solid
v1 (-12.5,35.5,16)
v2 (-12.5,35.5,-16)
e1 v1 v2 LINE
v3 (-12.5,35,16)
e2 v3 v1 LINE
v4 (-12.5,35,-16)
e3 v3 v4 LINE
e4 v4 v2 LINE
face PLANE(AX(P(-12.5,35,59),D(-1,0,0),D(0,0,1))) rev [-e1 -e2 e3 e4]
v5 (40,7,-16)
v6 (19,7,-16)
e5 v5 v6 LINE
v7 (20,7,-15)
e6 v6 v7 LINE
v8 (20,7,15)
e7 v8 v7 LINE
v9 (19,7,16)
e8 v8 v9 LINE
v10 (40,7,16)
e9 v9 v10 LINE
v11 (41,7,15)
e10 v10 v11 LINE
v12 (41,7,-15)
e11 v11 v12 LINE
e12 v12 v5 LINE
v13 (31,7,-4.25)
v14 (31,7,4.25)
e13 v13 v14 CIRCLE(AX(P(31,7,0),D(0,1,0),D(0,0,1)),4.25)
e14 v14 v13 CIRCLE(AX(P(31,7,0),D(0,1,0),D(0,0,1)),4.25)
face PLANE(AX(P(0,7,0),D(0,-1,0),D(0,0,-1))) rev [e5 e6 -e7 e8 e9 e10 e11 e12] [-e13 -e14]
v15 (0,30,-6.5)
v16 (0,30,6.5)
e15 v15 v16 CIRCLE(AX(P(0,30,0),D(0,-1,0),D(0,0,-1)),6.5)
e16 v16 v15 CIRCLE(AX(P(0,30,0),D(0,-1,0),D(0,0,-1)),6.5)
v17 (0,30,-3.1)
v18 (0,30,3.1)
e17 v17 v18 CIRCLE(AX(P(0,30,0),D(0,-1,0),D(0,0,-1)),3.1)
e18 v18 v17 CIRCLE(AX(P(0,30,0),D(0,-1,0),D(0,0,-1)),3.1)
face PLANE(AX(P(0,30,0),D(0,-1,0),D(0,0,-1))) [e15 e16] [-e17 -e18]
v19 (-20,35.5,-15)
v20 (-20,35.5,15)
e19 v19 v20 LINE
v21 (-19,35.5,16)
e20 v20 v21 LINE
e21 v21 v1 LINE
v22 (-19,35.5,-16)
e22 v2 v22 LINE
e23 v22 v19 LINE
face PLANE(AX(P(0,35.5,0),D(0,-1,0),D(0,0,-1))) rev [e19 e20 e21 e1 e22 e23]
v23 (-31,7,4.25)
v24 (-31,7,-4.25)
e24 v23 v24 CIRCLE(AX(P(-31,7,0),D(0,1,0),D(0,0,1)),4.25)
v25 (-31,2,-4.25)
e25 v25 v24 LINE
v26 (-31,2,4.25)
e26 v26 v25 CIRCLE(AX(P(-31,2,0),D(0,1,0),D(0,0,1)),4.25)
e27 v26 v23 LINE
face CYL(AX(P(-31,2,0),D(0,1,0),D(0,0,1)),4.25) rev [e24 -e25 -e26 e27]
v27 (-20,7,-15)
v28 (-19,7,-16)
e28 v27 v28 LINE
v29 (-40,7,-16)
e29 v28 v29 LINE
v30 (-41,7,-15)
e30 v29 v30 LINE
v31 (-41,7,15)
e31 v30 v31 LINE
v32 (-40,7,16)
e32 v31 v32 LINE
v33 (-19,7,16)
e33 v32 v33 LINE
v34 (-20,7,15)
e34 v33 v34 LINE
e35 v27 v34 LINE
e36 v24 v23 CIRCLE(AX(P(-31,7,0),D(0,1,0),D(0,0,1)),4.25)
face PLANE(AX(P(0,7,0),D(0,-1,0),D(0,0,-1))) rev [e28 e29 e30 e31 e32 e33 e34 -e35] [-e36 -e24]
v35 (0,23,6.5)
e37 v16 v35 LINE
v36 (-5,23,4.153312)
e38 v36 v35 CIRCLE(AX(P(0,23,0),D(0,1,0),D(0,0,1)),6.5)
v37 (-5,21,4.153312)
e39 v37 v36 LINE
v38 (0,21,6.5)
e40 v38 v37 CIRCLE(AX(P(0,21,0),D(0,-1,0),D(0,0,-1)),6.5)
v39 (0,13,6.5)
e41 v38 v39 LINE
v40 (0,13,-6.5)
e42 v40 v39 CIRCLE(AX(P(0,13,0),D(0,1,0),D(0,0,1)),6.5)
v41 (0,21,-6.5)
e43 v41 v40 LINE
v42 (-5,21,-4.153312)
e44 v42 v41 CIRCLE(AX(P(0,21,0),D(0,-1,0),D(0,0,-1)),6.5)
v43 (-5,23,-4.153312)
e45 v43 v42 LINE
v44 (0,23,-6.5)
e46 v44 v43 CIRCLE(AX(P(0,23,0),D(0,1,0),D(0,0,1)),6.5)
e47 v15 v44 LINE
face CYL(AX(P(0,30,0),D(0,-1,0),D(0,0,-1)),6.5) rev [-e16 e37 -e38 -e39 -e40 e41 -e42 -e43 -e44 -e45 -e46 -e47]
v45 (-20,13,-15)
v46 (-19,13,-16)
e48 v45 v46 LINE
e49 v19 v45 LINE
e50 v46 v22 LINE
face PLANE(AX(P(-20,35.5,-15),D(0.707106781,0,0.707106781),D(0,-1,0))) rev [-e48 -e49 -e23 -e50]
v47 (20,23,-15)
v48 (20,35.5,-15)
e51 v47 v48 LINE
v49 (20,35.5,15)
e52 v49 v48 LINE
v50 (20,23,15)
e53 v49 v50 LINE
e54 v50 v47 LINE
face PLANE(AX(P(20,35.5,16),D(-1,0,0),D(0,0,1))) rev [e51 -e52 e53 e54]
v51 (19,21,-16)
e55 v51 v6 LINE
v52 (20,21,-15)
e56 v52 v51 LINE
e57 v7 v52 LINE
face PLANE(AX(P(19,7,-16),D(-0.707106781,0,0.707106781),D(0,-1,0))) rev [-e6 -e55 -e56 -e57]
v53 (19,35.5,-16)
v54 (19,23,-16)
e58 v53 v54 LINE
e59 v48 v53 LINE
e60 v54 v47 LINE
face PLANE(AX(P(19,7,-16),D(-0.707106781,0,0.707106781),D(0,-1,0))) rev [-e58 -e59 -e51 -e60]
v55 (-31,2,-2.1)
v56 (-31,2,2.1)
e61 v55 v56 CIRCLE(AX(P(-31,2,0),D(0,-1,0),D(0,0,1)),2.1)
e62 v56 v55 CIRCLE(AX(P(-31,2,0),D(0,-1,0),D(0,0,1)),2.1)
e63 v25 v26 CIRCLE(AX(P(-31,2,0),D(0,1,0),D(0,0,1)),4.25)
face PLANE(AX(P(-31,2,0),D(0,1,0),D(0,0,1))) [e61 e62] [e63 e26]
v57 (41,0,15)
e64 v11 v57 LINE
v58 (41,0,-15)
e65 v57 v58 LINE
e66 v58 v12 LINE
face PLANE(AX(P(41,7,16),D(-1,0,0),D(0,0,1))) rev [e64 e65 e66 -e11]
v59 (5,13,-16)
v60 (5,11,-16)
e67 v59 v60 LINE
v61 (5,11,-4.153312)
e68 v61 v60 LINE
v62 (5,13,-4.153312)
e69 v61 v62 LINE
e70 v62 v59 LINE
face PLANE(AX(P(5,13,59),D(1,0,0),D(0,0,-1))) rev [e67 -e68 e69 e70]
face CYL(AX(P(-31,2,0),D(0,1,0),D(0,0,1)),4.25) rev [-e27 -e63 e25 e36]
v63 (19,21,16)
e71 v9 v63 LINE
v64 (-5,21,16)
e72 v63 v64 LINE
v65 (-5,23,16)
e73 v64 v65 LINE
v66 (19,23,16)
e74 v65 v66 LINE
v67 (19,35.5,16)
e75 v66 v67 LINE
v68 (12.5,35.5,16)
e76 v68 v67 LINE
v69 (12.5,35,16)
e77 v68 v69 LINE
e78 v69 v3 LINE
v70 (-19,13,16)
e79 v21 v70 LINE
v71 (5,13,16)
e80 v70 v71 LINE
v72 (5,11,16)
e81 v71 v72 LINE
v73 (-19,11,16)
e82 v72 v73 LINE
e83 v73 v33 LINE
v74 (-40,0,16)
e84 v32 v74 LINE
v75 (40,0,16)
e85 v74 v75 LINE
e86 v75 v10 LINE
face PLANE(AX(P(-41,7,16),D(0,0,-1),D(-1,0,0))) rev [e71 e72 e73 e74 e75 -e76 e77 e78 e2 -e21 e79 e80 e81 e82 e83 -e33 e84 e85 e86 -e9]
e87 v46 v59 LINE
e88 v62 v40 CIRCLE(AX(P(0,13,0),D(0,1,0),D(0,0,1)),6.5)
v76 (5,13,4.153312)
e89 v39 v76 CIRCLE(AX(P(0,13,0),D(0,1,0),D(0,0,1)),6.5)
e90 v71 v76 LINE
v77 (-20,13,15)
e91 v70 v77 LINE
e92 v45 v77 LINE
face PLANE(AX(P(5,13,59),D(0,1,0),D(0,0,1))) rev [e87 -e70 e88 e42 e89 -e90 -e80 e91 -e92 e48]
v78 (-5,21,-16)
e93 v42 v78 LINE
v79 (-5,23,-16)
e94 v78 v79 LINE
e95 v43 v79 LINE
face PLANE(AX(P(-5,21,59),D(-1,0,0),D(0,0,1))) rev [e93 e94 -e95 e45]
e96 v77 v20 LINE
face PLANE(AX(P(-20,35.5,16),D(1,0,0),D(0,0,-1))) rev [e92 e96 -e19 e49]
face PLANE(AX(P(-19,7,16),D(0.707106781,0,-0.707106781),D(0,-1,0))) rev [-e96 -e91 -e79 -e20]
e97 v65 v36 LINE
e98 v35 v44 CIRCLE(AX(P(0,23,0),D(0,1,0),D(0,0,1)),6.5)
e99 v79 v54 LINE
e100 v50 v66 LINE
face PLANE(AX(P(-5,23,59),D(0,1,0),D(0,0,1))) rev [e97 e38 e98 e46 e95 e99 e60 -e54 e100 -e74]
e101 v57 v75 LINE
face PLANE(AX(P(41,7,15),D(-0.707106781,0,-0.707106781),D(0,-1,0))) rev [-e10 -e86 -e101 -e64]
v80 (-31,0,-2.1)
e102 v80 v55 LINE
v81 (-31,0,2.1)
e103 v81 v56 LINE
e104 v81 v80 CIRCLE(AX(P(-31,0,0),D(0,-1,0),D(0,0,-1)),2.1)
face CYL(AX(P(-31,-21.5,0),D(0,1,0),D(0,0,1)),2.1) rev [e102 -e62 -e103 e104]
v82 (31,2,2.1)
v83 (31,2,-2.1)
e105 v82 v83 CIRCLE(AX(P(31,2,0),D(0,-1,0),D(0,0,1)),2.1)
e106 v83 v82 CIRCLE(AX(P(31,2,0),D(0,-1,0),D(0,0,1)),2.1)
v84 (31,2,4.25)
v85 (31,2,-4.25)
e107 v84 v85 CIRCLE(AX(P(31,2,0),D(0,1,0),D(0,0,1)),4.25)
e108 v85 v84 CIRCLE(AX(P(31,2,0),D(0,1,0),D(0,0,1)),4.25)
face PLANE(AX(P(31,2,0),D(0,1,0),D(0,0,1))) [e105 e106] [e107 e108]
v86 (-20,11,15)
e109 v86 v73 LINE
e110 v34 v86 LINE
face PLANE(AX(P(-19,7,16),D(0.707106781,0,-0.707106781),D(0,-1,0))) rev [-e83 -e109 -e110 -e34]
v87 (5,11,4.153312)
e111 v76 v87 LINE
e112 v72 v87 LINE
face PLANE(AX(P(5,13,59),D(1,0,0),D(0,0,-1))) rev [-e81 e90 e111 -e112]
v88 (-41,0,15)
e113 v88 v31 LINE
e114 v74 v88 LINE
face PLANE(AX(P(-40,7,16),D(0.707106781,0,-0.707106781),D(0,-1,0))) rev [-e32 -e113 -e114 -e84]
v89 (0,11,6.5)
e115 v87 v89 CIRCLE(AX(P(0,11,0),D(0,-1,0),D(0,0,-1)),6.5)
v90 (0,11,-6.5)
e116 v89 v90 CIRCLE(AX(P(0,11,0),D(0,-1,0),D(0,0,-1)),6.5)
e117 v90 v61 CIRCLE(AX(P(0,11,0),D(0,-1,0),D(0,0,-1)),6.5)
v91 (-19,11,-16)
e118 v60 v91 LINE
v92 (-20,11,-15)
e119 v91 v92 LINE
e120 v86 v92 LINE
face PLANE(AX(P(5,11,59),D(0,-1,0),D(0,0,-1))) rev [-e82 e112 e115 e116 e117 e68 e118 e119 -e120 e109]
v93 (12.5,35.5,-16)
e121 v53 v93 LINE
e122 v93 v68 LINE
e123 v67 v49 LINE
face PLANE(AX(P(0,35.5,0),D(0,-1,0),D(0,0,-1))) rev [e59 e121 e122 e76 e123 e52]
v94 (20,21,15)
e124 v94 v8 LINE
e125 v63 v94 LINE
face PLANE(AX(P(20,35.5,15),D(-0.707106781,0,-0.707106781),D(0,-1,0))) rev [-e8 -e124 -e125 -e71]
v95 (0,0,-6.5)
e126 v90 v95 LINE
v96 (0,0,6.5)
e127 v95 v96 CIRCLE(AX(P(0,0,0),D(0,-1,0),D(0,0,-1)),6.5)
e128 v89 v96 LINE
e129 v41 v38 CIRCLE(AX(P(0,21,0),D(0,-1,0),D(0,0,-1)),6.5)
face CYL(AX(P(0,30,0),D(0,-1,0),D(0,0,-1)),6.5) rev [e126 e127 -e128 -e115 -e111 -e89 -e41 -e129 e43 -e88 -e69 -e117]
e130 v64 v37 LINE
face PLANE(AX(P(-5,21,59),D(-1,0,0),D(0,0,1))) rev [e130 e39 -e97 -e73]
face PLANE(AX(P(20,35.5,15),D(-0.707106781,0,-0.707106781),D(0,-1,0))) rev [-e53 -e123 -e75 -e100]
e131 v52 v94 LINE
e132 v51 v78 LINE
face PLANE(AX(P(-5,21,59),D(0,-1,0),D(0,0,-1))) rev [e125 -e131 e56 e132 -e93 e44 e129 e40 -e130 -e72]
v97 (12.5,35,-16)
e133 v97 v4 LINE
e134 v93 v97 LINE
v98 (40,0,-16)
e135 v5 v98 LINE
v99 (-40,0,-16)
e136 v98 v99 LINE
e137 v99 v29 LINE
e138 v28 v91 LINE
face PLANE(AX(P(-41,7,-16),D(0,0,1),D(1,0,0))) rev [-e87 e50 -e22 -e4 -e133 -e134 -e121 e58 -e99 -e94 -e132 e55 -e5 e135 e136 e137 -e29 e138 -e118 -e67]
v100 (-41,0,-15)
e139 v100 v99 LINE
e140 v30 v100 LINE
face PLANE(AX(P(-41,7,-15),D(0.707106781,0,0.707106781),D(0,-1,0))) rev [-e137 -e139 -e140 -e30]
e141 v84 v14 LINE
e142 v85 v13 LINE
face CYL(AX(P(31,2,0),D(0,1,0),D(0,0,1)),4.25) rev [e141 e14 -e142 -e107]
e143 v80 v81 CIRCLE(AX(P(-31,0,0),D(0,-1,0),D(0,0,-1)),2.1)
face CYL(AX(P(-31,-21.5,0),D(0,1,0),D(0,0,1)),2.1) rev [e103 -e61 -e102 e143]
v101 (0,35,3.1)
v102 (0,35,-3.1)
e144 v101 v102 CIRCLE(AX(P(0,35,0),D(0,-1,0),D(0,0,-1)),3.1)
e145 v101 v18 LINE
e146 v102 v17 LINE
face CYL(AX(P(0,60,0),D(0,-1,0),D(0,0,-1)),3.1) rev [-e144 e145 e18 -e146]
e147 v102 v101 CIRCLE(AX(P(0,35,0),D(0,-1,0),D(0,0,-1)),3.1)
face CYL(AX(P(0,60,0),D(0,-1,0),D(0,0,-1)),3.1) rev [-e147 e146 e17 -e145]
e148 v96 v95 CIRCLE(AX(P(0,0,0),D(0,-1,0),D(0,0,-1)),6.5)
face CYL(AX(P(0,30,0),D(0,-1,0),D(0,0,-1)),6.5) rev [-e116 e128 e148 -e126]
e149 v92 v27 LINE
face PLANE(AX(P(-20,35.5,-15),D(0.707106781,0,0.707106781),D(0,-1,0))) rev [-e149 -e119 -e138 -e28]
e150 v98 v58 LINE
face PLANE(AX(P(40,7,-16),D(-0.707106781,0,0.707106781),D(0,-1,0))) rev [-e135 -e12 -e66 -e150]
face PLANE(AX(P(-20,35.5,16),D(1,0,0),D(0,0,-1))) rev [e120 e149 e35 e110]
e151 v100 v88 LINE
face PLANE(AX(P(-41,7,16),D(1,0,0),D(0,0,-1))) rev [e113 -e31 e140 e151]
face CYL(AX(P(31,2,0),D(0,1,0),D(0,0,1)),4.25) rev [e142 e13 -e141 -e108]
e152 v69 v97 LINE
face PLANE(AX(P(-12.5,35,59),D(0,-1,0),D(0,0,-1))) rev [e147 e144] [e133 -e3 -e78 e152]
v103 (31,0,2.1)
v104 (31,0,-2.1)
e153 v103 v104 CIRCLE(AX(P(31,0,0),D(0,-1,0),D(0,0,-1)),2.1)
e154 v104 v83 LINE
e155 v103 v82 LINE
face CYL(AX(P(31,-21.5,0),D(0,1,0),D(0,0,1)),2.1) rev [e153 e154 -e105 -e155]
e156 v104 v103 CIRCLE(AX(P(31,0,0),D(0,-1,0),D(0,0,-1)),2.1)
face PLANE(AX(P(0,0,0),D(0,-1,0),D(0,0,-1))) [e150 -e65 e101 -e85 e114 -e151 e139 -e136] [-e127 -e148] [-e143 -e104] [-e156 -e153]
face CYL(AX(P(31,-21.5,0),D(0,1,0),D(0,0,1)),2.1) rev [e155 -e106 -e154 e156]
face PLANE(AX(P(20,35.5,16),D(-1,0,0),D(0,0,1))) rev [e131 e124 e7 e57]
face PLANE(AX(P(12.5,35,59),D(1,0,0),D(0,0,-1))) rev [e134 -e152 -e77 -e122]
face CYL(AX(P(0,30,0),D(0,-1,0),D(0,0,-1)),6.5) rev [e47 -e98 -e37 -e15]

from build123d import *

# Parameters (mm, degrees)
SKETCH1_W           = 82
SKETCH1_H           = 32
BOSS_EXTRUDE1_DEPTH = 7
SKETCH2_W           = 40
SKETCH2_H           = 32
BOSS_EXTRUDE2_DEPTH = 28.5
SKETCH3_R           = 2.1
CUT_EXTRUDE1_DEPTH  = 28.5
SKETCH4_R           = 4.25
CUT_EXTRUDE2_DEPTH  = 5
SKETCH5_W           = 50
SKETCH5_H           = 2
SKETCH5_W_2         = 25
SKETCH5_H_2         = 1
CUT_EXTRUDE3_DEPTH  = 75
SKETCH6_R           = 6.5
CUT_EXTRUDE4_DEPTH  = 30
SKETCH7_R           = 3.1
CUT_EXTRUDE5_DEPTH  = 30
CHAMFER1_SIZE       = 1


with BuildPart() as part:
    # Sketch1 → Boss-Extrude1 (new body)
    with BuildSketch(Plane(origin=(0, 0, 0), x_dir=(1, 0, 0), z_dir=(0, 1, 0))):
        Rectangle(SKETCH1_W, SKETCH1_H)
    extrude(amount=BOSS_EXTRUDE1_DEPTH)

    # Sketch2 → Boss-Extrude2 (add)
    with BuildSketch(Plane(origin=(0, 7, 0), x_dir=(1, 0, 0), z_dir=(0, 1, 0))):
        Rectangle(SKETCH2_W, SKETCH2_H)
    extrude(amount=BOSS_EXTRUDE2_DEPTH)

    # Sketch3 → Cut-Extrude1 (cut)
    with BuildSketch(Plane(origin=(0, 7, 0), x_dir=(1, 0, 0), z_dir=(0, 1, 0))):
        with Locations(Location((31, 0, 0), (0, 0, 270))):
            Circle(SKETCH3_R)
        with Locations(Location((-31, 0, 0), (0, 0, 270))):
            Circle(SKETCH3_R)
    extrude(amount=-CUT_EXTRUDE1_DEPTH, mode=Mode.SUBTRACT)

    # Sketch4 → Cut-Extrude2 (cut)
    with BuildSketch(Plane(origin=(0, 7, 0), x_dir=(1, 0, 0), z_dir=(0, 1, 0))):
        with Locations(Location((-31, 0, 0), (0, 0, 270))):
            Circle(SKETCH4_R)
        with Locations(Location((31, 0, 0), (0, 0, 270))):
            Circle(SKETCH4_R)
    extrude(amount=-CUT_EXTRUDE2_DEPTH, mode=Mode.SUBTRACT)

    # Sketch5 → Cut-Extrude3 (cut)
    with BuildSketch(Plane(origin=(0, 0, -16), x_dir=(-1, 0, 0), z_dir=(0, 0, -1))):
        with Locations((20, 12)):
            Rectangle(SKETCH5_W, SKETCH5_H)
        with Locations((-20, 22)):
            Rectangle(SKETCH5_W, SKETCH5_H)
        with Locations((0, 35.5)):
            Rectangle(SKETCH5_W_2, SKETCH5_H_2)
    extrude(amount=-CUT_EXTRUDE3_DEPTH, mode=Mode.SUBTRACT)

    # Sketch6 → Cut-Extrude4 (cut)
    with BuildSketch(Plane.XZ):
        with Locations(Location((0, 0, 0), (0, 0, 270))):
            Circle(SKETCH6_R)
    extrude(amount=-CUT_EXTRUDE4_DEPTH, mode=Mode.SUBTRACT)

    # Sketch7 → Cut-Extrude5 (cut)
    with BuildSketch(Plane.XZ.offset(-30)):
        with Locations(Location((0, 0, 0), (0, 0, 270))):
            Circle(SKETCH7_R)
    extrude(amount=-CUT_EXTRUDE5_DEPTH, mode=Mode.SUBTRACT)

    # Chamfer1
    chamfer1_edges = [part.edges().sort_by_distance(p)[0] for p in [
        (20, 29.25, 16),
        (20, 29.25, -16),
        (-20, 24.25, -16),
        (-20, 24.25, 16),
        (-20, 9, 16),
        (-20, 9, -16),
        (20, 14, -16),
        (20, 14, 16),
        (41, 3.5, 16),
        (-41, 3.5, 16),
        (-41, 3.5, -16),
        (41, 3.5, -16),
    ]]
    chamfer(chamfer1_edges, length=CHAMFER1_SIZE)


solid = part.part
